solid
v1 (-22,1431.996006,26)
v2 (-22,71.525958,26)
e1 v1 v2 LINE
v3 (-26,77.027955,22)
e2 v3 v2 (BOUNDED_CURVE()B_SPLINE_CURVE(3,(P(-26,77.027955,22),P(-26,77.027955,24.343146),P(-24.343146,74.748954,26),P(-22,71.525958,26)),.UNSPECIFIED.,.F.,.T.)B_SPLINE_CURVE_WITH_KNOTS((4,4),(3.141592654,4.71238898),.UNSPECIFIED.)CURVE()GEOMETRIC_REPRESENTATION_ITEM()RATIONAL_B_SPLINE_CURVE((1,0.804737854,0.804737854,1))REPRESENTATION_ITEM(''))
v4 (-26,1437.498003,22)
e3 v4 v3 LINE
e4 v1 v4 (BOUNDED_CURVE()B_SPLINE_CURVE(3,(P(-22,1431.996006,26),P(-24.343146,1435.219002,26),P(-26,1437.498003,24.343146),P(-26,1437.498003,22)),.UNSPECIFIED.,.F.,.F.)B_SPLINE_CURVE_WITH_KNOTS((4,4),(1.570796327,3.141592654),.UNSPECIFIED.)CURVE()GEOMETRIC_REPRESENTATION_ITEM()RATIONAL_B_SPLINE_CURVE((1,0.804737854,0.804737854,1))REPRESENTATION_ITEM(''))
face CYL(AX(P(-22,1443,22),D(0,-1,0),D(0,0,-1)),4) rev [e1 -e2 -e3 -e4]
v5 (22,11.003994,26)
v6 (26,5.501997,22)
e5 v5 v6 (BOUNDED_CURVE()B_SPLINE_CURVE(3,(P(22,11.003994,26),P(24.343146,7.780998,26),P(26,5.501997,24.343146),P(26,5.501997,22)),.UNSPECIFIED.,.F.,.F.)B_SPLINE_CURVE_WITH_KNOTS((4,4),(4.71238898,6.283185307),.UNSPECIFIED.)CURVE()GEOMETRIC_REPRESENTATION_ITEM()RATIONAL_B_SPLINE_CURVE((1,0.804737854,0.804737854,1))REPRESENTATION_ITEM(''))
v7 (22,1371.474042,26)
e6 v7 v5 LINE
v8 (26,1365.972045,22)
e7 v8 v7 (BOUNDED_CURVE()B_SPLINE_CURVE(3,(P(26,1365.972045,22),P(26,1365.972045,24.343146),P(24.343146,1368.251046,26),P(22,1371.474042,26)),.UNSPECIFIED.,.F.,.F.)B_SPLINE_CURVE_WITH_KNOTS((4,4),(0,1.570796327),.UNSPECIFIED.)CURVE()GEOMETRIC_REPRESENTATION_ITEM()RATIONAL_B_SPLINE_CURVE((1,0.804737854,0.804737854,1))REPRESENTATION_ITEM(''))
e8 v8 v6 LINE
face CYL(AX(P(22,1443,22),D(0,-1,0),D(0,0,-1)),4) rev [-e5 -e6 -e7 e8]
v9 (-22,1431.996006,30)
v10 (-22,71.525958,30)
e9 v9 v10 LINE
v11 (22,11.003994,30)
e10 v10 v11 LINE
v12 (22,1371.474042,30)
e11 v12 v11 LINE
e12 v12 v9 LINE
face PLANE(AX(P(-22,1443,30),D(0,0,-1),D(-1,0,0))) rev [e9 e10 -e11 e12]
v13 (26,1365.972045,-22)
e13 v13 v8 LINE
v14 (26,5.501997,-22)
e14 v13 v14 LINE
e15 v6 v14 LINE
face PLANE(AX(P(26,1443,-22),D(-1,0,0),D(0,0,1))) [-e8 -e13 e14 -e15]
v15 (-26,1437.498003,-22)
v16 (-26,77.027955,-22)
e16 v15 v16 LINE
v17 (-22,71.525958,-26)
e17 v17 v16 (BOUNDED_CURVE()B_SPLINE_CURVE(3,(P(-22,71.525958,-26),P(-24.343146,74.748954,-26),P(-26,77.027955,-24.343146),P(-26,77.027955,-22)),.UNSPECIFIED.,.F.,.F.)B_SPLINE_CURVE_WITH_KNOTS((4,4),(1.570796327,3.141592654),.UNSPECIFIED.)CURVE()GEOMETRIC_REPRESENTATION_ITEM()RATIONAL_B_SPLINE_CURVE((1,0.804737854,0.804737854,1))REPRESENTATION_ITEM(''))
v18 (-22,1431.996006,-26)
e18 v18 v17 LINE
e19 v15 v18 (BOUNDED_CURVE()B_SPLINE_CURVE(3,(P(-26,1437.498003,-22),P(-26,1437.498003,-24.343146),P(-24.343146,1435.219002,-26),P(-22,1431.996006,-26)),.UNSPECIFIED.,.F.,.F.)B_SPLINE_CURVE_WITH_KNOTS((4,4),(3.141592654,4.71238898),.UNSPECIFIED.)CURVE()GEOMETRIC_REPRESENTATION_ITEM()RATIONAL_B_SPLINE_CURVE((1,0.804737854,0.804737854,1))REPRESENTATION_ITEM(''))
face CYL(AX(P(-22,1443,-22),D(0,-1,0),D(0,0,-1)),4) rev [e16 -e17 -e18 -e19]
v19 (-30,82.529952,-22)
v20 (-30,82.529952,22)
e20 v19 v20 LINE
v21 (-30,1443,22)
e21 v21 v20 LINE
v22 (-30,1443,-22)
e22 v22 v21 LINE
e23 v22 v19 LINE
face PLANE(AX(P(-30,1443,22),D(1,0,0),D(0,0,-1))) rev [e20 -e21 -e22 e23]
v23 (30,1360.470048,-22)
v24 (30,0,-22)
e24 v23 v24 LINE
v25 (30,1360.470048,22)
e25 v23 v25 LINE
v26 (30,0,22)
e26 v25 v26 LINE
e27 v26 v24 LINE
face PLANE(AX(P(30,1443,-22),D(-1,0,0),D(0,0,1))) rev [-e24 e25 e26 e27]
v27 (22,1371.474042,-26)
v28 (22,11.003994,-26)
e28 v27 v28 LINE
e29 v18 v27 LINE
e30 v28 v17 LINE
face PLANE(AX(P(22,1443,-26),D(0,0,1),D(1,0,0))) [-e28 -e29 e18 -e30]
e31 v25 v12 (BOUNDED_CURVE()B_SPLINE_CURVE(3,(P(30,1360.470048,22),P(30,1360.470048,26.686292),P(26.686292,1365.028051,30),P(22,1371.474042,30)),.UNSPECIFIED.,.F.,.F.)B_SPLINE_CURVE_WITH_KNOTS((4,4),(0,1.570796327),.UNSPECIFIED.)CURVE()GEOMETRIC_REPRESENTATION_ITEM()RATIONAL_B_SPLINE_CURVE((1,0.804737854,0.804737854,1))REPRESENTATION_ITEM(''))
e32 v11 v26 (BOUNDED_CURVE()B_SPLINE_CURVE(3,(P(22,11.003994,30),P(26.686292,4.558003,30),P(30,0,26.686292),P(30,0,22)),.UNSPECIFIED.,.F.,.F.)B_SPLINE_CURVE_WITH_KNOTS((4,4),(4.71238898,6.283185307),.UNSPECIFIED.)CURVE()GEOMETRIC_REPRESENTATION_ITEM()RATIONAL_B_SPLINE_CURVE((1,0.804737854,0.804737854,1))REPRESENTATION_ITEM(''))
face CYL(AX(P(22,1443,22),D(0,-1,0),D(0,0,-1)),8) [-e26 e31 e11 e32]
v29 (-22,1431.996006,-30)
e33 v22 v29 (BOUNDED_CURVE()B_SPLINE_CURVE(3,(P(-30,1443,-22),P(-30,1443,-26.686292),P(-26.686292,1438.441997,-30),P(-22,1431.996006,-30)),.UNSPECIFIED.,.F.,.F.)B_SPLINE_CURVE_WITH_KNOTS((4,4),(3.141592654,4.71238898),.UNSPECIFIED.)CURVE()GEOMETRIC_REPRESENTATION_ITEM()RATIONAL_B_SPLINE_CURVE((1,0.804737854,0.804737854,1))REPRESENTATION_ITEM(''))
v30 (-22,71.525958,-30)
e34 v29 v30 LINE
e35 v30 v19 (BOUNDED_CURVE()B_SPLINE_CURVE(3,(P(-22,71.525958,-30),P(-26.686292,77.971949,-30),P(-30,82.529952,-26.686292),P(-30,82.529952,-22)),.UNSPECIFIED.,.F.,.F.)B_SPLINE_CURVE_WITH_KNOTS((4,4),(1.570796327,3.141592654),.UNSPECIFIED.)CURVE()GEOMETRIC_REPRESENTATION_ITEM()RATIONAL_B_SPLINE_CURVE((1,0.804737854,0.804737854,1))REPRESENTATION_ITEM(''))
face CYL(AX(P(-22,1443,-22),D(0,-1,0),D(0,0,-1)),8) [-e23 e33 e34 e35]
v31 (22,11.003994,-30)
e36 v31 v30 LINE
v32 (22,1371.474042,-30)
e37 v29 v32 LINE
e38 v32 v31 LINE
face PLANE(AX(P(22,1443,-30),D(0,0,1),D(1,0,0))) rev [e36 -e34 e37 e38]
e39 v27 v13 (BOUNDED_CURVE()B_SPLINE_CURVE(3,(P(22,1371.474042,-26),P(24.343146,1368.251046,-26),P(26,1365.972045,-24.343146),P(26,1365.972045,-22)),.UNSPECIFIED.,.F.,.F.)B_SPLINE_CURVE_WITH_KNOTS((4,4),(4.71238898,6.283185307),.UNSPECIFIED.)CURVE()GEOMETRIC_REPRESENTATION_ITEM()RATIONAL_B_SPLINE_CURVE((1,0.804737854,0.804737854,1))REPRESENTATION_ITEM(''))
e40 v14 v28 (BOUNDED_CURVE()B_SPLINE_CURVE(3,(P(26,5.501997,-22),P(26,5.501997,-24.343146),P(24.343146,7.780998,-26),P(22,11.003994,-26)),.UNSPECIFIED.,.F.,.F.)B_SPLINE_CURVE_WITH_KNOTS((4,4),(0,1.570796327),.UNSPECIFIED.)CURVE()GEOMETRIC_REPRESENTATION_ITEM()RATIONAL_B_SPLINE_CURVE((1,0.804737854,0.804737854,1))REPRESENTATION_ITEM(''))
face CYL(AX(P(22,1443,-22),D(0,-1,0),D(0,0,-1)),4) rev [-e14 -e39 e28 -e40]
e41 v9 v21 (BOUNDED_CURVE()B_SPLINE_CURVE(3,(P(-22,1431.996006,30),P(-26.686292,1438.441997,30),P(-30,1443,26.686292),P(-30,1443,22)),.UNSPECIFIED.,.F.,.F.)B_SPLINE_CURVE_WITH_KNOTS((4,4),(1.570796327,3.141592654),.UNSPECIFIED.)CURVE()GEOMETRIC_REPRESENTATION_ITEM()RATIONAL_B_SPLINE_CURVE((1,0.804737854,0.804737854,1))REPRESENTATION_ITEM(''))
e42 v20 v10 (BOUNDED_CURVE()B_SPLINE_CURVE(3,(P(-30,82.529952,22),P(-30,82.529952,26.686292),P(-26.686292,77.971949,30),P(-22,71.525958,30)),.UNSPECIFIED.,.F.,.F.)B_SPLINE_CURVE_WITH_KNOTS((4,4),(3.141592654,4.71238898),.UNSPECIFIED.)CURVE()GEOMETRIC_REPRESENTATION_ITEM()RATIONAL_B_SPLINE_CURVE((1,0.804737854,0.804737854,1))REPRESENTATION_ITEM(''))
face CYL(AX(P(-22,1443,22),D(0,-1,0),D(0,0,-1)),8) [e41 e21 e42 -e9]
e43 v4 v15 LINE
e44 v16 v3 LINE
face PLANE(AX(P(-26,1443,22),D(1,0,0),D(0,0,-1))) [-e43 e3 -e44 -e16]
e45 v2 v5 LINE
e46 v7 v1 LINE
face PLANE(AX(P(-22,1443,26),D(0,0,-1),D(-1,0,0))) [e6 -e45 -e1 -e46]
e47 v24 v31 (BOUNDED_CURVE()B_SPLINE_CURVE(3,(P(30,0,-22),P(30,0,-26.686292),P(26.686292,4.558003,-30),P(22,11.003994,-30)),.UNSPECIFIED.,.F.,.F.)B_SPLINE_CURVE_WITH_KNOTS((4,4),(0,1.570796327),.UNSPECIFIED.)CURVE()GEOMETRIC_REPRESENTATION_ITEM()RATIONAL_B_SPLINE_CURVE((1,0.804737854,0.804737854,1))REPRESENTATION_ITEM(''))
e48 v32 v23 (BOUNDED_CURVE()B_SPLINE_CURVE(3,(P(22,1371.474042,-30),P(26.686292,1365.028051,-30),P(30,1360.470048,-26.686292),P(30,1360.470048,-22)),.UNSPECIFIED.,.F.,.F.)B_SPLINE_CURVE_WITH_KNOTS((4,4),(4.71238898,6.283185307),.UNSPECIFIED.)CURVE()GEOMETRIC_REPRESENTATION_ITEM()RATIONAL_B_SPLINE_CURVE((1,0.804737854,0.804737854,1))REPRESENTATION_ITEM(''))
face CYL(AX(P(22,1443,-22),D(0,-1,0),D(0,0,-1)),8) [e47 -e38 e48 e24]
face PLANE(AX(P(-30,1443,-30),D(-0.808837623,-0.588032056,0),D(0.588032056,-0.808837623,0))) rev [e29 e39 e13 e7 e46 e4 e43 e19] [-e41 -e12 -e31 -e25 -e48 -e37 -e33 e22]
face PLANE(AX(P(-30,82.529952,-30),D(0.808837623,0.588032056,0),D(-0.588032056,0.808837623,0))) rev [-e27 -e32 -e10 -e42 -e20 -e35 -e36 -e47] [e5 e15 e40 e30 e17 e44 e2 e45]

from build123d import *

# Parameters (mm, degrees)
GB_T_6728_2002_SQUARE_HOLLOW_SECTION_60_DEPTH = 1443
CUT_EXTRUDE1_DEPTH                            = 1445.558410034
CUT_EXTRUDE1_DEPTH_BACK                       = 1445.558410034


with BuildPart() as part:
    # Sketch1 → GB/T 6728-2002 square hollow section 60×60×4(1) (new body)
    with BuildSketch(Plane(origin=(0, 0, 0), x_dir=(-1, 0, 0), z_dir=(0, 1, 0))):
        with BuildLine():
            Line((-22, -30), (22, -30))
            ThreePointArc((22, -30), (27.656854249, -27.656854249), (30, -22))
            Line((30, -22), (30, 22))
            ThreePointArc((30, 22), (27.656854249, 27.656854249), (22, 30))
            Line((22, 30), (-22, 30))
            ThreePointArc((-22, 30), (-27.656854249, 27.656854249), (-30, 22))
            Line((-30, 22), (-30, -22))
            ThreePointArc((-30, -22), (-27.656854249, -27.656854249), (-22, -30))
        make_face()
        with BuildLine():
            Line((-22, -26), (22, -26))
            ThreePointArc((22, -26), (24.828427125, -24.828427125), (26, -22))
            Line((26, -22), (26, 22))
            ThreePointArc((26, 22), (24.828427125, 24.828427125), (22, 26))
            Line((22, 26), (-22, 26))
            ThreePointArc((-22, 26), (-24.828427125, 24.828427125), (-26, 22))
            Line((-26, 22), (-26, -22))
            ThreePointArc((-26, -22), (-24.828427125, -24.828427125), (-22, -26))
        make_face(mode=Mode.SUBTRACT)
    extrude(amount=GB_T_6728_2002_SQUARE_HOLLOW_SECTION_60_DEPTH)

    # Sketch2 → Cut-Extrude1 (cut, two sides: drawn at the far end of the back side and taken through both)
    with BuildSketch(Plane.XY.offset(30).offset(-CUT_EXTRUDE1_DEPTH_BACK)):
        Polygon((-30, 1443), (30, 1360.470047999), (30, 1443), align=None)
        Polygon((-30, 0), (-30, 82.529952001), (30, 0), align=None)
    extrude(amount=CUT_EXTRUDE1_DEPTH + CUT_EXTRUDE1_DEPTH_BACK, mode=Mode.SUBTRACT)


solid = part.part
